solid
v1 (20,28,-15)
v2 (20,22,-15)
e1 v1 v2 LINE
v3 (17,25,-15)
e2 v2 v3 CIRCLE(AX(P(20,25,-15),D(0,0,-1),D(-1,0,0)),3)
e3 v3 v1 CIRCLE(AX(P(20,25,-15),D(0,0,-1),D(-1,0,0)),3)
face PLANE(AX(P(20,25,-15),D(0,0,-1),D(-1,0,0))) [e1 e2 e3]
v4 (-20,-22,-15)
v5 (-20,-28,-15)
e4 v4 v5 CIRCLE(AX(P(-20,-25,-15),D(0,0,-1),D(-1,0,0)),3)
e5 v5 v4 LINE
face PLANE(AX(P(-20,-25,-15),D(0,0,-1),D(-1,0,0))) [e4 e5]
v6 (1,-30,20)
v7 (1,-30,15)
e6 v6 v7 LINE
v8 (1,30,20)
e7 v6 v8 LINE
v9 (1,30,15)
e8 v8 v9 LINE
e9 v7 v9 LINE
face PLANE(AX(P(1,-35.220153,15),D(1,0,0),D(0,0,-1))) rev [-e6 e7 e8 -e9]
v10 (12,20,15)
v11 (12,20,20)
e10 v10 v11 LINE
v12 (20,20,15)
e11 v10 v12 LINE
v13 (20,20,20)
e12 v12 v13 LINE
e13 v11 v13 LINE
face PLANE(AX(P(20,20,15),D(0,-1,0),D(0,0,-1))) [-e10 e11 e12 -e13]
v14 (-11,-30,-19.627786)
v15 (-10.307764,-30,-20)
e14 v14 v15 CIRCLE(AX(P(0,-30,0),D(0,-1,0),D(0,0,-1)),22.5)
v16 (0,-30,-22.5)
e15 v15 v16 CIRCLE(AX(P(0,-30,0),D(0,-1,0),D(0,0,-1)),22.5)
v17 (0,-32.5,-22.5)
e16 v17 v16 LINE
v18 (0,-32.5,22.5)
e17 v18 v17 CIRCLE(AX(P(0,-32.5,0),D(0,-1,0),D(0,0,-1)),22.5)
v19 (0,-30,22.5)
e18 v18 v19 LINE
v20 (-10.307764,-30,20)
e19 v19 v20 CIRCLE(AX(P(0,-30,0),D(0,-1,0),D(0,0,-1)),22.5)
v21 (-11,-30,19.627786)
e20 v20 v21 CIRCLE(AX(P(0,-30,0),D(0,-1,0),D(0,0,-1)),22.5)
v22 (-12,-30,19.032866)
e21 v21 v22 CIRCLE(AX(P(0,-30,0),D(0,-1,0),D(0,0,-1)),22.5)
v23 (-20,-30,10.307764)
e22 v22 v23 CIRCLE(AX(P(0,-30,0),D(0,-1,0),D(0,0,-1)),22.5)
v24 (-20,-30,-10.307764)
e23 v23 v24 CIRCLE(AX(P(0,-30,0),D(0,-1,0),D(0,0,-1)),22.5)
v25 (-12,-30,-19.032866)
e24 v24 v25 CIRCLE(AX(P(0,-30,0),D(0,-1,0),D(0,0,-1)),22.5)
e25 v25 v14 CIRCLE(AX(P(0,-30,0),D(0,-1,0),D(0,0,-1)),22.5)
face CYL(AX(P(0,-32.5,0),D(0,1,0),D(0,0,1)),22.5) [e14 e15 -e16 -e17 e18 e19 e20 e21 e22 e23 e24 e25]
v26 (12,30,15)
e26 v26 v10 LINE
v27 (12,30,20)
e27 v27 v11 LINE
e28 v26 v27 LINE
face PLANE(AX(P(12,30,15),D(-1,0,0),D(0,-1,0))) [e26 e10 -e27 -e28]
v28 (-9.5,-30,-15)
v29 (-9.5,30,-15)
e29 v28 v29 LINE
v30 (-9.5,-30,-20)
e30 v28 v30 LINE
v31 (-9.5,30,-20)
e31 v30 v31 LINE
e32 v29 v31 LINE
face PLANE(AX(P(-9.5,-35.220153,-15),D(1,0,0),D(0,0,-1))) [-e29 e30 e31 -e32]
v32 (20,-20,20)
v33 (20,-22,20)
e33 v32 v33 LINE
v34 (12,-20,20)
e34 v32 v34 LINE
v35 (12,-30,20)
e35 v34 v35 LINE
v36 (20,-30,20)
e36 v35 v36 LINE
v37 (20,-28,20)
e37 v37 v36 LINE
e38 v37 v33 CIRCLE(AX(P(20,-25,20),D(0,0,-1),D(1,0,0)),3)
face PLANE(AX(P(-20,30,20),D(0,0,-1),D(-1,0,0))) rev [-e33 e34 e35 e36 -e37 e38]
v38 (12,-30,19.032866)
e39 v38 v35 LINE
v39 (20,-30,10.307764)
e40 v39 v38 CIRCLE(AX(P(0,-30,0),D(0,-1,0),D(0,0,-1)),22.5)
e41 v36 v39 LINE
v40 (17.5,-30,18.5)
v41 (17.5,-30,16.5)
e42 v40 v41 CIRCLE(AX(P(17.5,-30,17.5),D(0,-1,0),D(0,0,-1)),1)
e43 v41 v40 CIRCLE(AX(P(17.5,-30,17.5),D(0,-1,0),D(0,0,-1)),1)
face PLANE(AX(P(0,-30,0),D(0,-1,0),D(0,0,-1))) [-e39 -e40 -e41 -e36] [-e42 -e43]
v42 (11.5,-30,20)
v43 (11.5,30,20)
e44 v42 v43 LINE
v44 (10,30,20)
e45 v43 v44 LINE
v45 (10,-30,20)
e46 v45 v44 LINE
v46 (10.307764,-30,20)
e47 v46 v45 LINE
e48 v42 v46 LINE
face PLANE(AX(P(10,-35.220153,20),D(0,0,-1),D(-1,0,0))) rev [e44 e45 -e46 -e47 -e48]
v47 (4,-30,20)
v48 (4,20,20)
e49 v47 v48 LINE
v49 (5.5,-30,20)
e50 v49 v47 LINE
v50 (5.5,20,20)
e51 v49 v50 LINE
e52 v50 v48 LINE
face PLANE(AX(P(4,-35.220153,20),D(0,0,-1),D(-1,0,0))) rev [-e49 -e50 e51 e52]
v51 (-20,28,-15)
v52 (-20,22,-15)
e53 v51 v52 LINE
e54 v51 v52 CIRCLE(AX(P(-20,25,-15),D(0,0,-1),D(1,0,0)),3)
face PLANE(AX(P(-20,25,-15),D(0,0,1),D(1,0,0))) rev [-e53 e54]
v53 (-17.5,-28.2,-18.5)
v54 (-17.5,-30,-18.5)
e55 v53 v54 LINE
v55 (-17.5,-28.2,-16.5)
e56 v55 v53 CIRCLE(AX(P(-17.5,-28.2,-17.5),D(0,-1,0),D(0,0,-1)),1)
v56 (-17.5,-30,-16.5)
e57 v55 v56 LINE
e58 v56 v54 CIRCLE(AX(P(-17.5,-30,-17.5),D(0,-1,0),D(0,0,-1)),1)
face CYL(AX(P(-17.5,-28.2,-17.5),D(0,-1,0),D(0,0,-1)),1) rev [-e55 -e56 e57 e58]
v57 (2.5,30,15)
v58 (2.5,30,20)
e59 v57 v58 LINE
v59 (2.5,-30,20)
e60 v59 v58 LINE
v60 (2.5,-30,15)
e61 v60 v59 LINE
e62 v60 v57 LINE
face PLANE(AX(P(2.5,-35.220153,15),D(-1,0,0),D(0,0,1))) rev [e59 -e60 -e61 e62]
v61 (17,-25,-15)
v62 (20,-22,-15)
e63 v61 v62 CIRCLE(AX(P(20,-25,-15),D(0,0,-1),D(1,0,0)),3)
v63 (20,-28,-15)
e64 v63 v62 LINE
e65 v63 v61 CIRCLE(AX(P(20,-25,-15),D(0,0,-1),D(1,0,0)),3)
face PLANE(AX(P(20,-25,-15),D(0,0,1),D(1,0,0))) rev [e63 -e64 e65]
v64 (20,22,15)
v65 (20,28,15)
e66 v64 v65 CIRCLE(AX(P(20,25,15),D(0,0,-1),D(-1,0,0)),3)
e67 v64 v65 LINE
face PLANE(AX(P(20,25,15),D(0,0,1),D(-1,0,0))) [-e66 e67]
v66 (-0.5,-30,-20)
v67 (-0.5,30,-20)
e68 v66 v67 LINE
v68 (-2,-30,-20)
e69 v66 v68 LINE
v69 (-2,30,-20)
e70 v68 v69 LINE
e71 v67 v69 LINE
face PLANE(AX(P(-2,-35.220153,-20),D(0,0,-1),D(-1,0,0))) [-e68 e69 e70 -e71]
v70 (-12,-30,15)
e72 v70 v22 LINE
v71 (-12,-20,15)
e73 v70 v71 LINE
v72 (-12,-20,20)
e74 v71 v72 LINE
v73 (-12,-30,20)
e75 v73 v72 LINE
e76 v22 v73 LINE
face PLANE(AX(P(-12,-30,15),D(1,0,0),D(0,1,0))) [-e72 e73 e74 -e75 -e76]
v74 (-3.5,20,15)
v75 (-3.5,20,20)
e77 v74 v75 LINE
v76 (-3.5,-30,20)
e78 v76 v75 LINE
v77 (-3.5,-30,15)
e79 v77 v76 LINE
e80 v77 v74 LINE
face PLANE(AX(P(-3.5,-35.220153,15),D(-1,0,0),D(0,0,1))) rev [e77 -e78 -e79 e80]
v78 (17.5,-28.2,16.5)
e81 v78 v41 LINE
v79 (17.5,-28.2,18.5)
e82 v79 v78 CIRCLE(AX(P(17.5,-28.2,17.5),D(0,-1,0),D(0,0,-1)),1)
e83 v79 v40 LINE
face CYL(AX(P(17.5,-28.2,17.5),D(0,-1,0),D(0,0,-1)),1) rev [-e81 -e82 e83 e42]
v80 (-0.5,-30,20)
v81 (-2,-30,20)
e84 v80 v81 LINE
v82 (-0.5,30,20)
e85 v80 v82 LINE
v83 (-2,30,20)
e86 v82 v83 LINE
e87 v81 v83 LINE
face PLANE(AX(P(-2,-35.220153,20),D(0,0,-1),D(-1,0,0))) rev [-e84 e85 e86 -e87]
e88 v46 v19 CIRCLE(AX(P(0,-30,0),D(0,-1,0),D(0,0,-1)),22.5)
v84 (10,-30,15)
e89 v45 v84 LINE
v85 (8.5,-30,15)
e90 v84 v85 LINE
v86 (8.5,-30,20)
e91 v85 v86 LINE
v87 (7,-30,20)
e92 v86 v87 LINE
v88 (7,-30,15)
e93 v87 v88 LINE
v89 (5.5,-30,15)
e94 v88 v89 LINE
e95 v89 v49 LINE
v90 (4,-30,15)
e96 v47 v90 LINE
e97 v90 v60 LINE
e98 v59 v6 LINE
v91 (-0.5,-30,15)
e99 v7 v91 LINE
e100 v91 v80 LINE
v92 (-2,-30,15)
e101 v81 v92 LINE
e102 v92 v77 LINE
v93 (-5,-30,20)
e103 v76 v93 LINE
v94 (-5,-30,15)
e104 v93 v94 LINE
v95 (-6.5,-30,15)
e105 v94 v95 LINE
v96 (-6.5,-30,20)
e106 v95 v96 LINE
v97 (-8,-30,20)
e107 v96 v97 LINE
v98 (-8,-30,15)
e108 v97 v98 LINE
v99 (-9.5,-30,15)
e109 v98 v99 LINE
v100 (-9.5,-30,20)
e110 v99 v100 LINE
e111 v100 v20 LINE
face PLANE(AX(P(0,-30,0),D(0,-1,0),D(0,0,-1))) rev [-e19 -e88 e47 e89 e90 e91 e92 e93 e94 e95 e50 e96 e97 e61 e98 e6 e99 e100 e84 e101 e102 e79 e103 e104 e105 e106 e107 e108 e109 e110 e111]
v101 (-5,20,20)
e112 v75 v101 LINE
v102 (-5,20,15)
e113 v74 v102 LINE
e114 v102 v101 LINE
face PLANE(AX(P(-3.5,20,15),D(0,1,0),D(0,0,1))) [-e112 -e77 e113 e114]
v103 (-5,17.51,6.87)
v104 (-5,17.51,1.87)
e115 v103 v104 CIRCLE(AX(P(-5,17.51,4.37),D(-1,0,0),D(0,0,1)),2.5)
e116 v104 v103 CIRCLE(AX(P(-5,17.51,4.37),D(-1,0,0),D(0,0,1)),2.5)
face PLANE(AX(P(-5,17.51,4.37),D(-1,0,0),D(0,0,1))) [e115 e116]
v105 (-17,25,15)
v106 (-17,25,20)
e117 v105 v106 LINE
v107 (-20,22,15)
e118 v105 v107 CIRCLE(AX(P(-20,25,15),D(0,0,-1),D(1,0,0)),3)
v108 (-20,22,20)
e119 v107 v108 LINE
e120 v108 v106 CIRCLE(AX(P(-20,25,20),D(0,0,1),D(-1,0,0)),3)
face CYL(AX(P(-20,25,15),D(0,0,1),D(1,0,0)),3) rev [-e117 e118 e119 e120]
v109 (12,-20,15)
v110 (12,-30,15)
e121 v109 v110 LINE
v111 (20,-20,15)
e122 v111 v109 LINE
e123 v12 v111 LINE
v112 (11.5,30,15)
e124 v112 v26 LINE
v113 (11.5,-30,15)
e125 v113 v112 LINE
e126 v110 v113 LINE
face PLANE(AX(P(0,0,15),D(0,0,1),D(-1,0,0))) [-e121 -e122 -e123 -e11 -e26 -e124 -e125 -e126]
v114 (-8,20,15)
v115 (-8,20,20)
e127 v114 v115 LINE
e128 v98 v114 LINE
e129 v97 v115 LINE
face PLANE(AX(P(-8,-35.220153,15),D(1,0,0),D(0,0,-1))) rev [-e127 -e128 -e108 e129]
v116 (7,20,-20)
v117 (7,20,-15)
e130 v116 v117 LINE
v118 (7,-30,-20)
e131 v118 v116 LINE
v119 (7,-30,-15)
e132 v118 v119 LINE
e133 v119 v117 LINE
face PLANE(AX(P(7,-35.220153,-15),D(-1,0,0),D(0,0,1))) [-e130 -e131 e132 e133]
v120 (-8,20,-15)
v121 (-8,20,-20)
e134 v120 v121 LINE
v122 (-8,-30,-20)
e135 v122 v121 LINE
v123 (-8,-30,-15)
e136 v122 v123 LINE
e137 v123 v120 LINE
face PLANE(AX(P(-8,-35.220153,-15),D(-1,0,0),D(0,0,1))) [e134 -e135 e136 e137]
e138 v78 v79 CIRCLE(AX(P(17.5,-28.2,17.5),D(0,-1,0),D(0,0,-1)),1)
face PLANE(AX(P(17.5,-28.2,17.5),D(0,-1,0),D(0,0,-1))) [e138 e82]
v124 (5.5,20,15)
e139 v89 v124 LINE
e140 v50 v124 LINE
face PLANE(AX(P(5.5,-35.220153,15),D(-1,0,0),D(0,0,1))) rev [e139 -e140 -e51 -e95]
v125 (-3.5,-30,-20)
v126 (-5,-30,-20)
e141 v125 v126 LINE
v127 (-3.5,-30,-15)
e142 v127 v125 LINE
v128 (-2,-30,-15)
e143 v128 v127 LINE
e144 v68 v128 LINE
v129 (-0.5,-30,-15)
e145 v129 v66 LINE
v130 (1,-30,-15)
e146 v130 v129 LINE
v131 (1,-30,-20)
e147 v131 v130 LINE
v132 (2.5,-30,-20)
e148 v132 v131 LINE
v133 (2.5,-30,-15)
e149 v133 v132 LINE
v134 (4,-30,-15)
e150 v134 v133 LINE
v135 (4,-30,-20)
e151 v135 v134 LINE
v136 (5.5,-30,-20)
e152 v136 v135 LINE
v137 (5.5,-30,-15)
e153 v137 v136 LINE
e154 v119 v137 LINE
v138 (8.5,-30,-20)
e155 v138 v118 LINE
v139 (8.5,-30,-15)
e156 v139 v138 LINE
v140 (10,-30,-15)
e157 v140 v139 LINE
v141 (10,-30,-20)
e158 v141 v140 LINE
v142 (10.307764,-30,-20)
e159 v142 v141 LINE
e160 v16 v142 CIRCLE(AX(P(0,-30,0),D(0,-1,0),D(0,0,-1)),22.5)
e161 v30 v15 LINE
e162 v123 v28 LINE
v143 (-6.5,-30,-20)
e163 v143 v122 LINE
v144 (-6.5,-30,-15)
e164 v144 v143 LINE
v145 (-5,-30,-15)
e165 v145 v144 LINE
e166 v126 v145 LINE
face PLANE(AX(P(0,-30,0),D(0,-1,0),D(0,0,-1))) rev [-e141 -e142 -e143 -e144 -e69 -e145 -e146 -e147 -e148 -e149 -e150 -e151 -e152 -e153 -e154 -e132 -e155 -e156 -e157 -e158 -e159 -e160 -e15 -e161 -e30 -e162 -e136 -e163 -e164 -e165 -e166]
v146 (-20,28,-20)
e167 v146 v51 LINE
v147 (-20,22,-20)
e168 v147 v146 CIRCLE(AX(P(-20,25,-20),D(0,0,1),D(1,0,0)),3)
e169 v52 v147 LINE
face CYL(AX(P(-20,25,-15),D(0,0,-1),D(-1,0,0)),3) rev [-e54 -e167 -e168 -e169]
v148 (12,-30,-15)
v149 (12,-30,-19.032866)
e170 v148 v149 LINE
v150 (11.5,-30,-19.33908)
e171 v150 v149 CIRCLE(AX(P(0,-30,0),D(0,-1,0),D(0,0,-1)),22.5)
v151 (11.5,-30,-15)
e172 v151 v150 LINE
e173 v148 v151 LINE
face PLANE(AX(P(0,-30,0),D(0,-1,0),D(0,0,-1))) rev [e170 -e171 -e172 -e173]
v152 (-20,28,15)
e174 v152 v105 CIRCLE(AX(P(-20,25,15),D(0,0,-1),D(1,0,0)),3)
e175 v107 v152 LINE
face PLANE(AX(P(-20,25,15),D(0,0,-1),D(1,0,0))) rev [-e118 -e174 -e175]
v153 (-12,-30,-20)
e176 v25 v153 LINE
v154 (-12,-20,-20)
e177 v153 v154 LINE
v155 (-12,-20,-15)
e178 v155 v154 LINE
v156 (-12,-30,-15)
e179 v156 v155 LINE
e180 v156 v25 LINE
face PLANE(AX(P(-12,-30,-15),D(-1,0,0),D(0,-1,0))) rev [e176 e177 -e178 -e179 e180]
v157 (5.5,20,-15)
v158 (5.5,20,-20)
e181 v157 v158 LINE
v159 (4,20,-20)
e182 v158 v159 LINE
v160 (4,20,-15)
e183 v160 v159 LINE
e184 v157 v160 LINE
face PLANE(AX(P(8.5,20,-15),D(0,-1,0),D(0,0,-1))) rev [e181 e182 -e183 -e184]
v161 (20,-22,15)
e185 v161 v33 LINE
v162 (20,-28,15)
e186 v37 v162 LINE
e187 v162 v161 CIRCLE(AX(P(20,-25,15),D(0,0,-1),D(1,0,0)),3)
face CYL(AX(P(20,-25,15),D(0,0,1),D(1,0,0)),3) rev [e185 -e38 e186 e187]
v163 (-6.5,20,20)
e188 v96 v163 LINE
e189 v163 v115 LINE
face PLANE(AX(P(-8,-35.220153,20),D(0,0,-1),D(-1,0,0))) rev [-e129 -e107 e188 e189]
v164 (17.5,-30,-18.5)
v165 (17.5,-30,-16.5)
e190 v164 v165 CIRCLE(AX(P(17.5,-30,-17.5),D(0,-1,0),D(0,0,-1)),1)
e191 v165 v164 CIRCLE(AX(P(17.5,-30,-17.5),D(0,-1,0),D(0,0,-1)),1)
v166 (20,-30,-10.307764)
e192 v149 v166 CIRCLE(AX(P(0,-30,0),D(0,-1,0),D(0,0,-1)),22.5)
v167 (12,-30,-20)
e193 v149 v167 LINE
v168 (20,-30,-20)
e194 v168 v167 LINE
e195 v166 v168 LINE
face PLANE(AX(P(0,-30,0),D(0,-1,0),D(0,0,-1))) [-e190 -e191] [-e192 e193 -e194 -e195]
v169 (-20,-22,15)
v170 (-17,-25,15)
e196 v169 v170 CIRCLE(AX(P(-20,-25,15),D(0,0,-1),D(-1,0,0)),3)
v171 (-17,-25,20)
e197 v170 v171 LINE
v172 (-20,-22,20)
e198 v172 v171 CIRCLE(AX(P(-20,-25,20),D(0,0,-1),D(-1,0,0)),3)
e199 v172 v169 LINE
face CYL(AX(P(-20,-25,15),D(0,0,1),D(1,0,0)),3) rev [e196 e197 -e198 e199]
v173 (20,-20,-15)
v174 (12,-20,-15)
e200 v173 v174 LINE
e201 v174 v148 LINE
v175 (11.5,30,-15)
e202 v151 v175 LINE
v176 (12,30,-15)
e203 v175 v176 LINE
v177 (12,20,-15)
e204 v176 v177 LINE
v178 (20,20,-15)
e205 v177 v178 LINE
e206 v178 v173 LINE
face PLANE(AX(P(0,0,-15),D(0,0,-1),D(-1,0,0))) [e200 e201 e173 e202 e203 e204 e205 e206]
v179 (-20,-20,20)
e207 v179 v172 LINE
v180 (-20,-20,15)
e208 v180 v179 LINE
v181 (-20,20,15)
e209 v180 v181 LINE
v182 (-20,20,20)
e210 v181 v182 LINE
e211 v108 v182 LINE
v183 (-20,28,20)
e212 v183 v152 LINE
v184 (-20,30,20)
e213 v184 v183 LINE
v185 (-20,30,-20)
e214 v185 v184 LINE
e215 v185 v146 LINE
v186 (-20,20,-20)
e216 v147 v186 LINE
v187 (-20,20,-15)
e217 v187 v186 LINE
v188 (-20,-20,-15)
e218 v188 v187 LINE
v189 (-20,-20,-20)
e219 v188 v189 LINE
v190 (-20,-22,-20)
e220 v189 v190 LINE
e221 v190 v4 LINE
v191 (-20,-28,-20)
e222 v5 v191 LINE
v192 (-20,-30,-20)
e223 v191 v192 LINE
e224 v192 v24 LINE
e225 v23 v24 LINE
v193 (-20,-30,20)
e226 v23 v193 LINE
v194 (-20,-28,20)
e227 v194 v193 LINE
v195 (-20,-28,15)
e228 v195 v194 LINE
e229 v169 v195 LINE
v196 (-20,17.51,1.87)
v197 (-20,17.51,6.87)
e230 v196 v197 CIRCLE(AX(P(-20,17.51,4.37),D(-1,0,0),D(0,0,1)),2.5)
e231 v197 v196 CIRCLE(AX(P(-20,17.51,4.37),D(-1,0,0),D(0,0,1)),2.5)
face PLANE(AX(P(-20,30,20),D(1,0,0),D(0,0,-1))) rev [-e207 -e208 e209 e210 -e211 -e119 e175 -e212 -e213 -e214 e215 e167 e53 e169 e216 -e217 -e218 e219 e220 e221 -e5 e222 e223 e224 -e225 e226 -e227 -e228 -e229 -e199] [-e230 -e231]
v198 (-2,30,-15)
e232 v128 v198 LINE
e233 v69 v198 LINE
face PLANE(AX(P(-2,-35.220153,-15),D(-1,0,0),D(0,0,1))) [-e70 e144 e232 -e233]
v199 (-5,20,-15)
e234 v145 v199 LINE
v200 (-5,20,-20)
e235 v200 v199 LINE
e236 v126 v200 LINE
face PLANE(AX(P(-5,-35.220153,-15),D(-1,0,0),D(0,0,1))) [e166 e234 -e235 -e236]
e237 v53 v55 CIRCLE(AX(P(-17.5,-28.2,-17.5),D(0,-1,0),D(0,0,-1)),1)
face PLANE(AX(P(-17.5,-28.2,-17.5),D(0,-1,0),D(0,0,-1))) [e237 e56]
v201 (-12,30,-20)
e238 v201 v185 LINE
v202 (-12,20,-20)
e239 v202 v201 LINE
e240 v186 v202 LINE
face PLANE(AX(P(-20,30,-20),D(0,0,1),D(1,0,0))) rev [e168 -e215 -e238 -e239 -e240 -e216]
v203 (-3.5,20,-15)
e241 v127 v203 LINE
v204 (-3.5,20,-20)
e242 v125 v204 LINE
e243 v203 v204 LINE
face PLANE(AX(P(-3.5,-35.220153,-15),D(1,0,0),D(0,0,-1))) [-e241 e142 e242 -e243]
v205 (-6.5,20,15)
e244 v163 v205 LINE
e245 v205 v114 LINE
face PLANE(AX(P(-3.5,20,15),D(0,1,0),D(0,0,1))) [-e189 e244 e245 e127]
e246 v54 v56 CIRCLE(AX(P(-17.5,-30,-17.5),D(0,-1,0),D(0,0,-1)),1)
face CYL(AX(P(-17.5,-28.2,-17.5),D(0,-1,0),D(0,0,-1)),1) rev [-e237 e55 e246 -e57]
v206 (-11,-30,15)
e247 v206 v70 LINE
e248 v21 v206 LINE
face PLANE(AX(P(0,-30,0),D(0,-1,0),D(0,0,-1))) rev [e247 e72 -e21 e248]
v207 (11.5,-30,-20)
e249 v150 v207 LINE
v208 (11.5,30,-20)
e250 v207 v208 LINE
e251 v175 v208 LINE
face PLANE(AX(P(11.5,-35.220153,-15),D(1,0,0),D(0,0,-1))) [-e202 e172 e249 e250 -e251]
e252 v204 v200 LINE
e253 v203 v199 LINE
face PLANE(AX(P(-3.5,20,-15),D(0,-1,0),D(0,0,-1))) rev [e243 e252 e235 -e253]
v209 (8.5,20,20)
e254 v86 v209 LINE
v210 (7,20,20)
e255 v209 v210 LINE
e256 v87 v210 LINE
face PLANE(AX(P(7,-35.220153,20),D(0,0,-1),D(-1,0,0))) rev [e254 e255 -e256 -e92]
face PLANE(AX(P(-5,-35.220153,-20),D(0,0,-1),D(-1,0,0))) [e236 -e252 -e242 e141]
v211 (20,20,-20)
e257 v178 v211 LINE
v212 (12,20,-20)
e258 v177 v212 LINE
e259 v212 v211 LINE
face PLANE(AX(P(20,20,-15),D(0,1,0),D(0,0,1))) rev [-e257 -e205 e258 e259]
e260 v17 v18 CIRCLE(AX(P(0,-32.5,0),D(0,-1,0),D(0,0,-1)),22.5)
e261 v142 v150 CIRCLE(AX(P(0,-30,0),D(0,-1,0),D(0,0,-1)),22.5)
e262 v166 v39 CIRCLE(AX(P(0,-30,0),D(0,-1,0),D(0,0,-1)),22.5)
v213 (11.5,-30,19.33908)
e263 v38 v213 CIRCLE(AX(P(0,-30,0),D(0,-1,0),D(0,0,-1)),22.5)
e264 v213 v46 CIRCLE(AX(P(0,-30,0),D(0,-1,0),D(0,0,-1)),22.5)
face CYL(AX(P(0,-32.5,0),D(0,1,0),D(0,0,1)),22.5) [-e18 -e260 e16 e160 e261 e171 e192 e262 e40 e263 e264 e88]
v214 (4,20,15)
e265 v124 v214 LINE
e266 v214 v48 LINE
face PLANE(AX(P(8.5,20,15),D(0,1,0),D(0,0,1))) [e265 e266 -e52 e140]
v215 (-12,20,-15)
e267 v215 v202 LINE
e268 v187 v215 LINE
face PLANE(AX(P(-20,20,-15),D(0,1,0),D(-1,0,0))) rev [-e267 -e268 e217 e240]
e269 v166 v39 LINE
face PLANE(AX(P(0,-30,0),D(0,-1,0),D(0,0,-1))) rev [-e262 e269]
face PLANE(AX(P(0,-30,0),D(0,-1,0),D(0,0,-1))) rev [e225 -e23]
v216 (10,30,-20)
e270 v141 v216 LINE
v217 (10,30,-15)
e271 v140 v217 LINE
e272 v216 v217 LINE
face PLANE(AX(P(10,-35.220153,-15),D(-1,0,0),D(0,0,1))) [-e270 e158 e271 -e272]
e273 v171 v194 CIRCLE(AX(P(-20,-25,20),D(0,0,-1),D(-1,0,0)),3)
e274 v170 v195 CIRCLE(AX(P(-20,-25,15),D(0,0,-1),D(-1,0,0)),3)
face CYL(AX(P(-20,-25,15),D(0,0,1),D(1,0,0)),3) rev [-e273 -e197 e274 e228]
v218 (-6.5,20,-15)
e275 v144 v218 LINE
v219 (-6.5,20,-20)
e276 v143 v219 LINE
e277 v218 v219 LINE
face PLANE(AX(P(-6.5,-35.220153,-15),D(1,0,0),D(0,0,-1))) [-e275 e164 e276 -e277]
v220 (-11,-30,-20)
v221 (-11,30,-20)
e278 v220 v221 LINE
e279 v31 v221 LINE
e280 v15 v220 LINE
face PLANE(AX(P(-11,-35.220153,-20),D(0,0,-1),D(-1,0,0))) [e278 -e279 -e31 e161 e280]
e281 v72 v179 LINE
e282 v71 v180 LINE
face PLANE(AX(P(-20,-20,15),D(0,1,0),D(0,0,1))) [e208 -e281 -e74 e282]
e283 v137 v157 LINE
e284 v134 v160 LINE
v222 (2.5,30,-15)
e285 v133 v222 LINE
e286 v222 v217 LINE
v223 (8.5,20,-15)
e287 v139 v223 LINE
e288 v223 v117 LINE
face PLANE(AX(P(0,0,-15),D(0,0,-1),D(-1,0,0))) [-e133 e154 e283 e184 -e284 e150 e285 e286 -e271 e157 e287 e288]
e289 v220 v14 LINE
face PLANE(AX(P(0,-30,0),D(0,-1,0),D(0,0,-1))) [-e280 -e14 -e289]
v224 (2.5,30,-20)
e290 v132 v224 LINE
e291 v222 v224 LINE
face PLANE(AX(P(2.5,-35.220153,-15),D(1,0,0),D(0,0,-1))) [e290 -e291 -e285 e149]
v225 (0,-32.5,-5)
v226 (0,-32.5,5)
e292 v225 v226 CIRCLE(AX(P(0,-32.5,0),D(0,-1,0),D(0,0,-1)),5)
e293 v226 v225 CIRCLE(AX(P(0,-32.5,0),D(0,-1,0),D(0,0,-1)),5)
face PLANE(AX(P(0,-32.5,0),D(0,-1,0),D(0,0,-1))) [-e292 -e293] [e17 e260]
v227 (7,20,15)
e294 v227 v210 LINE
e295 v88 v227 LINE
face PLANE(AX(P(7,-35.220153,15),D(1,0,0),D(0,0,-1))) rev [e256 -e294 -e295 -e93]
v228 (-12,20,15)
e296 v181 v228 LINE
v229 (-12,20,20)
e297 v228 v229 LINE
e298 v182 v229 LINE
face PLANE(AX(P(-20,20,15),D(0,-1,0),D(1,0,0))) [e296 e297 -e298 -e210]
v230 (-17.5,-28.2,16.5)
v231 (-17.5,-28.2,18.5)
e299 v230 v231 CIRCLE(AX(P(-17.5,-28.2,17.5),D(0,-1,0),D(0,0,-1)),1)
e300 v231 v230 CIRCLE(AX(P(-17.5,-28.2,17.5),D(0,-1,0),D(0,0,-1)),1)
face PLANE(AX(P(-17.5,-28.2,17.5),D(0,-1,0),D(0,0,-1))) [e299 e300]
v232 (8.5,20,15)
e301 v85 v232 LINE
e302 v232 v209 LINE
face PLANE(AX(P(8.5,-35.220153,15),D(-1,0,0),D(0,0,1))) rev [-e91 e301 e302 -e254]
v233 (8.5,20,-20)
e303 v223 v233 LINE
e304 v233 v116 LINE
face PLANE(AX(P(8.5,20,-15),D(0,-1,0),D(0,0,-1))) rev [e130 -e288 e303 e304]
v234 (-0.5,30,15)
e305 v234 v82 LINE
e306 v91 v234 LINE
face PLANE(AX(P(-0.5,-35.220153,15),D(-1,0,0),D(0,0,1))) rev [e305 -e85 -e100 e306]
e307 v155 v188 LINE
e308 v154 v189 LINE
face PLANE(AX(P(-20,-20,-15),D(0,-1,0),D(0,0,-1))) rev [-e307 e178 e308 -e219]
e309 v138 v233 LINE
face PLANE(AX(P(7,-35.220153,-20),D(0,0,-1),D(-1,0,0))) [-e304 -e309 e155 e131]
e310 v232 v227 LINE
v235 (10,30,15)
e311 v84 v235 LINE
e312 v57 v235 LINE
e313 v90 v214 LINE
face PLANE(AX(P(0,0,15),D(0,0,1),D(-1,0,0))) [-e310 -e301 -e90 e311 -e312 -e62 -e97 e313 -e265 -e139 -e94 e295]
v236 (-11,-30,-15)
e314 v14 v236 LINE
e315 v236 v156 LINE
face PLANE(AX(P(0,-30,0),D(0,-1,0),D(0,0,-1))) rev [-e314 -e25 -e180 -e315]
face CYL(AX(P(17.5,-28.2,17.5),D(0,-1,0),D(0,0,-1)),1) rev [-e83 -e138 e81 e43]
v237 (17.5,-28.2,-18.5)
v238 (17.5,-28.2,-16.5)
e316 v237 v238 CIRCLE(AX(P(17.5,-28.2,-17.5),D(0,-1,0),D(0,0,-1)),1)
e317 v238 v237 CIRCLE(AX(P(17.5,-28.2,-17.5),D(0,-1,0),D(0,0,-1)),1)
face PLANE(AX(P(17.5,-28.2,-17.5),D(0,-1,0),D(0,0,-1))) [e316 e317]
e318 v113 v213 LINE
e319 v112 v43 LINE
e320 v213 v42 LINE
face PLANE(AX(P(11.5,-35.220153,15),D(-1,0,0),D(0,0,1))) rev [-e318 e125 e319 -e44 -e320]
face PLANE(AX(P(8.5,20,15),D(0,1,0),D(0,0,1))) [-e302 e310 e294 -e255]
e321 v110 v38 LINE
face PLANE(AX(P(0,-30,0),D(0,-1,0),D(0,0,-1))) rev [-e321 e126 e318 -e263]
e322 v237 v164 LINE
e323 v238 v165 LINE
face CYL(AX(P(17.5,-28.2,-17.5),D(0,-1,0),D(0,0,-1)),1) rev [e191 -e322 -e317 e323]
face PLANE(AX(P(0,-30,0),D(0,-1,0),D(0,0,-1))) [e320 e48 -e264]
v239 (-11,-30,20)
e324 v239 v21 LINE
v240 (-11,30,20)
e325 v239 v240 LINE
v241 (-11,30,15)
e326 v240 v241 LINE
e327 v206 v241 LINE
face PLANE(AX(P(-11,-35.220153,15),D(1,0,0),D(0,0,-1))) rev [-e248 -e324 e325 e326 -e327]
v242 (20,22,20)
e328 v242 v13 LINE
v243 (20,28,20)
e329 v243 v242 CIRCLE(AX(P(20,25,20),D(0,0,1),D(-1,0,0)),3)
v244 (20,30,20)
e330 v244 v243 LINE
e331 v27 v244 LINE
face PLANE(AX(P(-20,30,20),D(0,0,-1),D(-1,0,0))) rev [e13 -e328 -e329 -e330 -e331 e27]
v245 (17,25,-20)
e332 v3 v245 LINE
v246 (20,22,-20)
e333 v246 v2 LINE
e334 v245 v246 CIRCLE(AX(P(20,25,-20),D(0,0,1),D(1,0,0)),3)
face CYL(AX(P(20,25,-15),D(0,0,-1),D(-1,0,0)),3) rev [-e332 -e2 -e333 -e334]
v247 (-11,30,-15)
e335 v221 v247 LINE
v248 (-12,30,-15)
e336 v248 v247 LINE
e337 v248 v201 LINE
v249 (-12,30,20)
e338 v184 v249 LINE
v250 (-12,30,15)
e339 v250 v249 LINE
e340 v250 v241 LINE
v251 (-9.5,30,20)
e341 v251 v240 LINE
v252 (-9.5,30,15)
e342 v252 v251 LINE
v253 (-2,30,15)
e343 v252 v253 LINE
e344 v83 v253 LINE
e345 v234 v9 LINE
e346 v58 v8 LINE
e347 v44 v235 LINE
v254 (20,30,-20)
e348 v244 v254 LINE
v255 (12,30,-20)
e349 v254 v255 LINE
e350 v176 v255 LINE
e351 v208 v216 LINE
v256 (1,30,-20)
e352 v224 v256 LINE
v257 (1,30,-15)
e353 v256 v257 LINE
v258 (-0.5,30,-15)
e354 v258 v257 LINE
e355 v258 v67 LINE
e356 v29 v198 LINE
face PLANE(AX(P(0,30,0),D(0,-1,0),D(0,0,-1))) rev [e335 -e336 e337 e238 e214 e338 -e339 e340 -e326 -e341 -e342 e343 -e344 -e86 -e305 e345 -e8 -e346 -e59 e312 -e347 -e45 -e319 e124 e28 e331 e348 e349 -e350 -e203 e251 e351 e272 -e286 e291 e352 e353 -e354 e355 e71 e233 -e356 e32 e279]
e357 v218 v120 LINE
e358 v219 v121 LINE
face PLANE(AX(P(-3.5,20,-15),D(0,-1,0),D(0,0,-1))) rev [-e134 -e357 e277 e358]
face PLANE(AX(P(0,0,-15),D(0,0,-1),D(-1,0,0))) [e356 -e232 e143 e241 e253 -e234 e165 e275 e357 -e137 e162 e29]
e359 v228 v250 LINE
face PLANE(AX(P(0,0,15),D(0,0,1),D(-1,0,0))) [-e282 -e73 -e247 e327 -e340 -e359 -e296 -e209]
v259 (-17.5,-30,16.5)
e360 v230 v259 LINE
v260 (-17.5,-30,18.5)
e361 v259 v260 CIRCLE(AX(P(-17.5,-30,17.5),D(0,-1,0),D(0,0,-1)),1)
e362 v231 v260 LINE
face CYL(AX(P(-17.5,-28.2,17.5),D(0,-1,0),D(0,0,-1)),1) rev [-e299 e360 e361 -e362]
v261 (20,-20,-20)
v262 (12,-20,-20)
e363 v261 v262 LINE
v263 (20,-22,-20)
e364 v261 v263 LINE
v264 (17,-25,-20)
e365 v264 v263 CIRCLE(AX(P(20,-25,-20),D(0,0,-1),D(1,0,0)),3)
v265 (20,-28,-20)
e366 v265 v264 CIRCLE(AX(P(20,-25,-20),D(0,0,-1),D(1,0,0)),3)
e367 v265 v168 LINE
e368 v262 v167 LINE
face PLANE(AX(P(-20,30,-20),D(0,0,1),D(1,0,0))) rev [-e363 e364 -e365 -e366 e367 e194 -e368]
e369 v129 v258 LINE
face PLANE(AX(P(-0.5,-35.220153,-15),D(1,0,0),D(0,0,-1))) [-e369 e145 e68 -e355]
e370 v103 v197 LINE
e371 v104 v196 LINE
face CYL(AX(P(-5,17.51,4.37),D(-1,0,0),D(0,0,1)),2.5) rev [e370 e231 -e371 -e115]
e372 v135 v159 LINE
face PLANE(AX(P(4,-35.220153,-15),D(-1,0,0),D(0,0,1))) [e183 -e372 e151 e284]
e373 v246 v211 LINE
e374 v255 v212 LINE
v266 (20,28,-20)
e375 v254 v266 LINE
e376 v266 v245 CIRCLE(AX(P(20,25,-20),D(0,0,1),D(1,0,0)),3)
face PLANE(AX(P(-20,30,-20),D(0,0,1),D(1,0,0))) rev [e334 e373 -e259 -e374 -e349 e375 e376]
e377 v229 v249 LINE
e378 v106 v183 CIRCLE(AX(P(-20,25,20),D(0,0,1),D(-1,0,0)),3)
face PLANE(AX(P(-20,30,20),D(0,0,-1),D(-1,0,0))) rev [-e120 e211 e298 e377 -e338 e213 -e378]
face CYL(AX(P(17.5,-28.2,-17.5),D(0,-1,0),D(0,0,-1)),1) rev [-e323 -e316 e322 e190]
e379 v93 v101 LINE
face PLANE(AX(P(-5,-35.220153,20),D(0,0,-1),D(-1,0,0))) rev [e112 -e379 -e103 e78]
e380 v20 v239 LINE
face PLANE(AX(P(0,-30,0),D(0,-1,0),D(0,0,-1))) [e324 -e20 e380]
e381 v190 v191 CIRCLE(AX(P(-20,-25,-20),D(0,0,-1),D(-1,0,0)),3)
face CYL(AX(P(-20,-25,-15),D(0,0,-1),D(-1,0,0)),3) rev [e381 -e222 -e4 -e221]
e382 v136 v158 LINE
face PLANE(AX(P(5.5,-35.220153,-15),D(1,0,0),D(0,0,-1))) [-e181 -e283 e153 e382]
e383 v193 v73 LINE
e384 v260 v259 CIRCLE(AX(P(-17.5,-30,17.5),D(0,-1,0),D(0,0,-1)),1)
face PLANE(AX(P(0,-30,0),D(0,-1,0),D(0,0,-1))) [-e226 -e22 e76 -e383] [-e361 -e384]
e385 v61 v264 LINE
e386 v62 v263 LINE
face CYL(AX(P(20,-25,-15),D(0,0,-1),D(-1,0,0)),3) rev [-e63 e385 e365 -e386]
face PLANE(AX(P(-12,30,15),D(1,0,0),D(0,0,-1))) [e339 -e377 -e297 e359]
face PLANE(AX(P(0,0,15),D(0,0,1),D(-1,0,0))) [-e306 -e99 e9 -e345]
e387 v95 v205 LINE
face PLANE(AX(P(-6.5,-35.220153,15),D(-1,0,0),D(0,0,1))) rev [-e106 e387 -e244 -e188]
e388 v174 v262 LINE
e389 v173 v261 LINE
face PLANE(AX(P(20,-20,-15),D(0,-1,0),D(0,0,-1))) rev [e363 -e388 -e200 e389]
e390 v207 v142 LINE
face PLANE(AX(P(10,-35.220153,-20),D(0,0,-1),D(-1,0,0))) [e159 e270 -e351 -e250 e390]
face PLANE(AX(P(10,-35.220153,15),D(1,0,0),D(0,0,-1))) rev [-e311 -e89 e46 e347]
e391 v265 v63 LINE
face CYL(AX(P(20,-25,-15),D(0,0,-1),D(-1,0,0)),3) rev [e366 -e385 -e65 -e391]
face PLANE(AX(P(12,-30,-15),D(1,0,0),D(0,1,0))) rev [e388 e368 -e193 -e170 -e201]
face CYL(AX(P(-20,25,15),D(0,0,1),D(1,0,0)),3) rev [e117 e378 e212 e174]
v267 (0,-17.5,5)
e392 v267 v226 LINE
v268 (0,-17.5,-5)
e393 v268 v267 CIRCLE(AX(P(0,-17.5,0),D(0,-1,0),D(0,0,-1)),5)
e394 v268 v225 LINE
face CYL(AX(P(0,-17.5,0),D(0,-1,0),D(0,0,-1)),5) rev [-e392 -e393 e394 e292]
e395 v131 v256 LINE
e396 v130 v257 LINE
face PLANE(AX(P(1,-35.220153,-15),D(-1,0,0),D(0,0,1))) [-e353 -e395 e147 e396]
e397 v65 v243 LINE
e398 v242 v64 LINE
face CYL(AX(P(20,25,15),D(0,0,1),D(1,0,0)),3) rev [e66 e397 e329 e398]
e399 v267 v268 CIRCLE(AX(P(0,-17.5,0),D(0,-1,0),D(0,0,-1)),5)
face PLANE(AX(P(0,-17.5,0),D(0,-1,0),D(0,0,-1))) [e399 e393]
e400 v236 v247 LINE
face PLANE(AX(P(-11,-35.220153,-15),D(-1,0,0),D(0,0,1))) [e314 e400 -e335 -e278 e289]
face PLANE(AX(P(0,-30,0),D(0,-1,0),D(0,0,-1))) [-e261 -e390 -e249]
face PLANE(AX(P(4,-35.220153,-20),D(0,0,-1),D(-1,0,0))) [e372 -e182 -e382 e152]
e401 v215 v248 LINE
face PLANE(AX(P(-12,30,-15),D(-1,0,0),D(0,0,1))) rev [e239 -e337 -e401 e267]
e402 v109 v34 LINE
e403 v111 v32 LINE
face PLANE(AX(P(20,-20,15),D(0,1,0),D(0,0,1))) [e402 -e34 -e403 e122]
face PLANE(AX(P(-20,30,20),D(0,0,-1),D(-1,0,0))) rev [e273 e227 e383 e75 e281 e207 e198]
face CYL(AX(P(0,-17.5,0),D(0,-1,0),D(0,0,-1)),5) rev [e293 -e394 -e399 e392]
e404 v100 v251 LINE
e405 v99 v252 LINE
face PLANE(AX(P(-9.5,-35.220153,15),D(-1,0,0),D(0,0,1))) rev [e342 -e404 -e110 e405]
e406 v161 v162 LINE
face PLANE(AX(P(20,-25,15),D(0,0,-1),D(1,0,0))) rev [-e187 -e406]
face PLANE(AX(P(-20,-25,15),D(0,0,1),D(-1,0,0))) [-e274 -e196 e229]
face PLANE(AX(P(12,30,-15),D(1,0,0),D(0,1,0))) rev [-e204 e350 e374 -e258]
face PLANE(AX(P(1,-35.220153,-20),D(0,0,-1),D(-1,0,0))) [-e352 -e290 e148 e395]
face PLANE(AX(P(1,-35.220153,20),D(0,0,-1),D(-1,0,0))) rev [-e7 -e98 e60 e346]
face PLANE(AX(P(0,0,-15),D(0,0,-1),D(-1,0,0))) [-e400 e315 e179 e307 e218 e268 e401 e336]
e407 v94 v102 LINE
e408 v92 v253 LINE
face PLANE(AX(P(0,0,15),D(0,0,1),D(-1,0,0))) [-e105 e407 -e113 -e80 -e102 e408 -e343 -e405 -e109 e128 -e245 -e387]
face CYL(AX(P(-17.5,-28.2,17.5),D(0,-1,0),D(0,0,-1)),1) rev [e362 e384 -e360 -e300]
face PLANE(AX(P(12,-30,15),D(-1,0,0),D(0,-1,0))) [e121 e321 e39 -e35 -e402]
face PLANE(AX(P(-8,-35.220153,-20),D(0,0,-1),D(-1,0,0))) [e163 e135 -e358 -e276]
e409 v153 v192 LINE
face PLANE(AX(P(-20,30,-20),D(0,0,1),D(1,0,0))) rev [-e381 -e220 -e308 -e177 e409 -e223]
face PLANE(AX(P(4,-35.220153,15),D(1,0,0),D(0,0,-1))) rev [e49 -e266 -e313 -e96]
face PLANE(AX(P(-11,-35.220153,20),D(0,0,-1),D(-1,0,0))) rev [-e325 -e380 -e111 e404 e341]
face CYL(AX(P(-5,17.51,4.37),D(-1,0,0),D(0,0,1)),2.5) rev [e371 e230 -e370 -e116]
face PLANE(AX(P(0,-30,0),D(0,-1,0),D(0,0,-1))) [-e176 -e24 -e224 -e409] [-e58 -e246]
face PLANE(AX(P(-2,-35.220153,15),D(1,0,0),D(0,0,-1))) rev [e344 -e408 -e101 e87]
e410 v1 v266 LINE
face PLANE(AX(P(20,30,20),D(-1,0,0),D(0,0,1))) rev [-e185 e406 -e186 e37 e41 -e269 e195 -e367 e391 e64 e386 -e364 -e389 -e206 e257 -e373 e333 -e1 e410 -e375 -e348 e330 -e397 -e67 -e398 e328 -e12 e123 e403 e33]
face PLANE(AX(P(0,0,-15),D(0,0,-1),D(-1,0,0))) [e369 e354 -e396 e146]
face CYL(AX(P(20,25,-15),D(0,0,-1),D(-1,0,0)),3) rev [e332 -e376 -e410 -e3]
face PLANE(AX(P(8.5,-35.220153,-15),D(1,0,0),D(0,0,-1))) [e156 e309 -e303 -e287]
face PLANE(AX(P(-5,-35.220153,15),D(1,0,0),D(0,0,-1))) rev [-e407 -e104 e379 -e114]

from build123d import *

# Parameters (mm, degrees)
SKETCH1_W           = 40
SKETCH1_H           = 40
BOSS_EXTRUDE1_DEPTH = 30
CUT_EXTRUDE1_DEPTH  = 5
SKETCH3_W           = 1.5
SKETCH3_H           = 5
BOSS_EXTRUDE2_DEPTH = 60
SKETCH4_W           = 4.5
SKETCH4_H           = 10
CUT_EXTRUDE2_DEPTH  = 5
SKETCH5_R           = 3
CUT_EXTRUDE3_DEPTH  = 5
SKETCH6_R           = 22.5
BOSS_EXTRUDE3_DEPTH = 2.5
SKETCH7_R           = 5
CUT_EXTRUDE4_DEPTH  = 15
SKETCH8_R           = 2.5
CUT_EXTRUDE6_DEPTH  = 15
SKETCH9_R           = 1
CUT_EXTRUDE7_DEPTH  = 1.8


with BuildPart() as part:
    # Sketch1 → Boss-Extrude1 (new, symmetric)
    with BuildSketch(Plane(origin=(0, 0, 0), x_dir=(1, 0, 0), z_dir=(0, 1, 0))):
        Rectangle(SKETCH1_W, SKETCH1_H)
    extrude(amount=BOSS_EXTRUDE1_DEPTH, both=True)

    # Sketch2 → Cut-Extrude1 (cut)
    with BuildSketch(Plane(origin=(0, 0, -20), x_dir=(-1, 0, 0), z_dir=(0, 0, -1))):
        Polygon((-12, 30), (12, 30), (12, 20), (20, 20), (20, -20), (12, -20), (12, -30), (-12, -30), (-12, -20), (-20, -20), (-20, 20), (-12, 20), align=None)
    cut_extrude1 = extrude(amount=-CUT_EXTRUDE1_DEPTH, mode=Mode.SUBTRACT)

    # Mirror1: Cut-Extrude1 across plane
    add(cut_extrude1.mirror(Plane.XY), mode=Mode.SUBTRACT)

    # Sketch3 → Boss-Extrude2 (add)
    with BuildSketch(Plane(origin=(0, 30, 0), x_dir=(1, 0, 0), z_dir=(0, 1, 0))):
        with Locations((-10.25, 17.5)):
            Rectangle(SKETCH3_W, SKETCH3_H)
        with Locations((-7.25, 17.5)):
            Rectangle(SKETCH3_W, SKETCH3_H)
        with Locations((-4.25, 17.5)):
            Rectangle(SKETCH3_W, SKETCH3_H)
        with Locations((-1.25, 17.5)):
            Rectangle(SKETCH3_W, SKETCH3_H)
        with Locations((1.75, 17.5)):
            Rectangle(SKETCH3_W, SKETCH3_H)
        with Locations((4.75, 17.5)):
            Rectangle(SKETCH3_W, SKETCH3_H)
        with Locations((7.75, 17.5)):
            Rectangle(SKETCH3_W, SKETCH3_H)
        with Locations((10.75, 17.5)):
            Rectangle(SKETCH3_W, SKETCH3_H)
    boss_extrude2 = extrude(amount=-BOSS_EXTRUDE2_DEPTH)

    # Sketch4 → Cut-Extrude2 (cut)
    with BuildSketch(Plane(origin=(0, 0, -20), x_dir=(-1, 0, 0), z_dir=(0, 0, -1))):
        with Locations((-6.25, 25)):
            Rectangle(SKETCH4_W, SKETCH4_H)
        with Locations((5.75, 25)):
            Rectangle(SKETCH4_W, SKETCH4_H)
    cut_extrude2 = extrude(amount=-CUT_EXTRUDE2_DEPTH, mode=Mode.SUBTRACT)

    # Mirror2: Boss-Extrude2, Cut-Extrude2 across plane
    add(boss_extrude2.mirror(Plane.XY))
    add(cut_extrude2.mirror(Plane.XY), mode=Mode.SUBTRACT)

    # Sketch5 → Cut-Extrude3 (cut)
    with BuildSketch(Plane(origin=(0, 0, -20), x_dir=(-1, 0, 0), z_dir=(0, 0, -1))):
        with Locations((-20, 25)):
            Circle(SKETCH5_R)
        with Locations((20, 25)):
            Circle(SKETCH5_R)
        with Locations((-20, -25)):
            Circle(SKETCH5_R)
        with Locations((20, -25)):
            Circle(SKETCH5_R)
    cut_extrude3 = extrude(amount=-CUT_EXTRUDE3_DEPTH, mode=Mode.SUBTRACT)

    # Mirror3: Cut-Extrude3 across plane
    add(cut_extrude3.mirror(Plane.XY), mode=Mode.SUBTRACT)

    # Sketch6 → Boss-Extrude3 (add)
    with BuildSketch(Plane.XZ.offset(30)):
        with Locations(Location((0, 0, 0), (0, 0, 62.733955549))):
            Circle(SKETCH6_R)
    extrude(amount=BOSS_EXTRUDE3_DEPTH)

    # Sketch7 → Cut-Extrude4 (cut)
    with BuildSketch(Plane.XZ.offset(32.5)):
        with Locations(Location((0, 0, 0), (0, 0, 270))):
            Circle(SKETCH7_R)
    extrude(amount=-CUT_EXTRUDE4_DEPTH, mode=Mode.SUBTRACT)

    # Sketch8 → Cut-Extrude6 (cut)
    with BuildSketch(Plane.ZY.offset(20)):
        with Locations((4.37, 17.51)):
            Circle(SKETCH8_R)
    extrude(amount=-CUT_EXTRUDE6_DEPTH, mode=Mode.SUBTRACT)

    # Sketch9 → Cut-Extrude7 (cut)
    with BuildSketch(Plane.XZ.offset(30)):
        with Locations(Location((-17.5, 17.5, 0), (0, 0, 270))):
            Circle(SKETCH9_R)
        with Locations(Location((-17.5, -17.5, 0), (0, 0, 270))):
            Circle(SKETCH9_R)
        with Locations(Location((17.5, -17.5, 0), (0, 0, 270))):
            Circle(SKETCH9_R)
        with Locations(Location((17.5, 17.5, 0), (0, 0, 270))):
            Circle(SKETCH9_R)
    extrude(amount=-CUT_EXTRUDE7_DEPTH, mode=Mode.SUBTRACT)


solid = part.part
